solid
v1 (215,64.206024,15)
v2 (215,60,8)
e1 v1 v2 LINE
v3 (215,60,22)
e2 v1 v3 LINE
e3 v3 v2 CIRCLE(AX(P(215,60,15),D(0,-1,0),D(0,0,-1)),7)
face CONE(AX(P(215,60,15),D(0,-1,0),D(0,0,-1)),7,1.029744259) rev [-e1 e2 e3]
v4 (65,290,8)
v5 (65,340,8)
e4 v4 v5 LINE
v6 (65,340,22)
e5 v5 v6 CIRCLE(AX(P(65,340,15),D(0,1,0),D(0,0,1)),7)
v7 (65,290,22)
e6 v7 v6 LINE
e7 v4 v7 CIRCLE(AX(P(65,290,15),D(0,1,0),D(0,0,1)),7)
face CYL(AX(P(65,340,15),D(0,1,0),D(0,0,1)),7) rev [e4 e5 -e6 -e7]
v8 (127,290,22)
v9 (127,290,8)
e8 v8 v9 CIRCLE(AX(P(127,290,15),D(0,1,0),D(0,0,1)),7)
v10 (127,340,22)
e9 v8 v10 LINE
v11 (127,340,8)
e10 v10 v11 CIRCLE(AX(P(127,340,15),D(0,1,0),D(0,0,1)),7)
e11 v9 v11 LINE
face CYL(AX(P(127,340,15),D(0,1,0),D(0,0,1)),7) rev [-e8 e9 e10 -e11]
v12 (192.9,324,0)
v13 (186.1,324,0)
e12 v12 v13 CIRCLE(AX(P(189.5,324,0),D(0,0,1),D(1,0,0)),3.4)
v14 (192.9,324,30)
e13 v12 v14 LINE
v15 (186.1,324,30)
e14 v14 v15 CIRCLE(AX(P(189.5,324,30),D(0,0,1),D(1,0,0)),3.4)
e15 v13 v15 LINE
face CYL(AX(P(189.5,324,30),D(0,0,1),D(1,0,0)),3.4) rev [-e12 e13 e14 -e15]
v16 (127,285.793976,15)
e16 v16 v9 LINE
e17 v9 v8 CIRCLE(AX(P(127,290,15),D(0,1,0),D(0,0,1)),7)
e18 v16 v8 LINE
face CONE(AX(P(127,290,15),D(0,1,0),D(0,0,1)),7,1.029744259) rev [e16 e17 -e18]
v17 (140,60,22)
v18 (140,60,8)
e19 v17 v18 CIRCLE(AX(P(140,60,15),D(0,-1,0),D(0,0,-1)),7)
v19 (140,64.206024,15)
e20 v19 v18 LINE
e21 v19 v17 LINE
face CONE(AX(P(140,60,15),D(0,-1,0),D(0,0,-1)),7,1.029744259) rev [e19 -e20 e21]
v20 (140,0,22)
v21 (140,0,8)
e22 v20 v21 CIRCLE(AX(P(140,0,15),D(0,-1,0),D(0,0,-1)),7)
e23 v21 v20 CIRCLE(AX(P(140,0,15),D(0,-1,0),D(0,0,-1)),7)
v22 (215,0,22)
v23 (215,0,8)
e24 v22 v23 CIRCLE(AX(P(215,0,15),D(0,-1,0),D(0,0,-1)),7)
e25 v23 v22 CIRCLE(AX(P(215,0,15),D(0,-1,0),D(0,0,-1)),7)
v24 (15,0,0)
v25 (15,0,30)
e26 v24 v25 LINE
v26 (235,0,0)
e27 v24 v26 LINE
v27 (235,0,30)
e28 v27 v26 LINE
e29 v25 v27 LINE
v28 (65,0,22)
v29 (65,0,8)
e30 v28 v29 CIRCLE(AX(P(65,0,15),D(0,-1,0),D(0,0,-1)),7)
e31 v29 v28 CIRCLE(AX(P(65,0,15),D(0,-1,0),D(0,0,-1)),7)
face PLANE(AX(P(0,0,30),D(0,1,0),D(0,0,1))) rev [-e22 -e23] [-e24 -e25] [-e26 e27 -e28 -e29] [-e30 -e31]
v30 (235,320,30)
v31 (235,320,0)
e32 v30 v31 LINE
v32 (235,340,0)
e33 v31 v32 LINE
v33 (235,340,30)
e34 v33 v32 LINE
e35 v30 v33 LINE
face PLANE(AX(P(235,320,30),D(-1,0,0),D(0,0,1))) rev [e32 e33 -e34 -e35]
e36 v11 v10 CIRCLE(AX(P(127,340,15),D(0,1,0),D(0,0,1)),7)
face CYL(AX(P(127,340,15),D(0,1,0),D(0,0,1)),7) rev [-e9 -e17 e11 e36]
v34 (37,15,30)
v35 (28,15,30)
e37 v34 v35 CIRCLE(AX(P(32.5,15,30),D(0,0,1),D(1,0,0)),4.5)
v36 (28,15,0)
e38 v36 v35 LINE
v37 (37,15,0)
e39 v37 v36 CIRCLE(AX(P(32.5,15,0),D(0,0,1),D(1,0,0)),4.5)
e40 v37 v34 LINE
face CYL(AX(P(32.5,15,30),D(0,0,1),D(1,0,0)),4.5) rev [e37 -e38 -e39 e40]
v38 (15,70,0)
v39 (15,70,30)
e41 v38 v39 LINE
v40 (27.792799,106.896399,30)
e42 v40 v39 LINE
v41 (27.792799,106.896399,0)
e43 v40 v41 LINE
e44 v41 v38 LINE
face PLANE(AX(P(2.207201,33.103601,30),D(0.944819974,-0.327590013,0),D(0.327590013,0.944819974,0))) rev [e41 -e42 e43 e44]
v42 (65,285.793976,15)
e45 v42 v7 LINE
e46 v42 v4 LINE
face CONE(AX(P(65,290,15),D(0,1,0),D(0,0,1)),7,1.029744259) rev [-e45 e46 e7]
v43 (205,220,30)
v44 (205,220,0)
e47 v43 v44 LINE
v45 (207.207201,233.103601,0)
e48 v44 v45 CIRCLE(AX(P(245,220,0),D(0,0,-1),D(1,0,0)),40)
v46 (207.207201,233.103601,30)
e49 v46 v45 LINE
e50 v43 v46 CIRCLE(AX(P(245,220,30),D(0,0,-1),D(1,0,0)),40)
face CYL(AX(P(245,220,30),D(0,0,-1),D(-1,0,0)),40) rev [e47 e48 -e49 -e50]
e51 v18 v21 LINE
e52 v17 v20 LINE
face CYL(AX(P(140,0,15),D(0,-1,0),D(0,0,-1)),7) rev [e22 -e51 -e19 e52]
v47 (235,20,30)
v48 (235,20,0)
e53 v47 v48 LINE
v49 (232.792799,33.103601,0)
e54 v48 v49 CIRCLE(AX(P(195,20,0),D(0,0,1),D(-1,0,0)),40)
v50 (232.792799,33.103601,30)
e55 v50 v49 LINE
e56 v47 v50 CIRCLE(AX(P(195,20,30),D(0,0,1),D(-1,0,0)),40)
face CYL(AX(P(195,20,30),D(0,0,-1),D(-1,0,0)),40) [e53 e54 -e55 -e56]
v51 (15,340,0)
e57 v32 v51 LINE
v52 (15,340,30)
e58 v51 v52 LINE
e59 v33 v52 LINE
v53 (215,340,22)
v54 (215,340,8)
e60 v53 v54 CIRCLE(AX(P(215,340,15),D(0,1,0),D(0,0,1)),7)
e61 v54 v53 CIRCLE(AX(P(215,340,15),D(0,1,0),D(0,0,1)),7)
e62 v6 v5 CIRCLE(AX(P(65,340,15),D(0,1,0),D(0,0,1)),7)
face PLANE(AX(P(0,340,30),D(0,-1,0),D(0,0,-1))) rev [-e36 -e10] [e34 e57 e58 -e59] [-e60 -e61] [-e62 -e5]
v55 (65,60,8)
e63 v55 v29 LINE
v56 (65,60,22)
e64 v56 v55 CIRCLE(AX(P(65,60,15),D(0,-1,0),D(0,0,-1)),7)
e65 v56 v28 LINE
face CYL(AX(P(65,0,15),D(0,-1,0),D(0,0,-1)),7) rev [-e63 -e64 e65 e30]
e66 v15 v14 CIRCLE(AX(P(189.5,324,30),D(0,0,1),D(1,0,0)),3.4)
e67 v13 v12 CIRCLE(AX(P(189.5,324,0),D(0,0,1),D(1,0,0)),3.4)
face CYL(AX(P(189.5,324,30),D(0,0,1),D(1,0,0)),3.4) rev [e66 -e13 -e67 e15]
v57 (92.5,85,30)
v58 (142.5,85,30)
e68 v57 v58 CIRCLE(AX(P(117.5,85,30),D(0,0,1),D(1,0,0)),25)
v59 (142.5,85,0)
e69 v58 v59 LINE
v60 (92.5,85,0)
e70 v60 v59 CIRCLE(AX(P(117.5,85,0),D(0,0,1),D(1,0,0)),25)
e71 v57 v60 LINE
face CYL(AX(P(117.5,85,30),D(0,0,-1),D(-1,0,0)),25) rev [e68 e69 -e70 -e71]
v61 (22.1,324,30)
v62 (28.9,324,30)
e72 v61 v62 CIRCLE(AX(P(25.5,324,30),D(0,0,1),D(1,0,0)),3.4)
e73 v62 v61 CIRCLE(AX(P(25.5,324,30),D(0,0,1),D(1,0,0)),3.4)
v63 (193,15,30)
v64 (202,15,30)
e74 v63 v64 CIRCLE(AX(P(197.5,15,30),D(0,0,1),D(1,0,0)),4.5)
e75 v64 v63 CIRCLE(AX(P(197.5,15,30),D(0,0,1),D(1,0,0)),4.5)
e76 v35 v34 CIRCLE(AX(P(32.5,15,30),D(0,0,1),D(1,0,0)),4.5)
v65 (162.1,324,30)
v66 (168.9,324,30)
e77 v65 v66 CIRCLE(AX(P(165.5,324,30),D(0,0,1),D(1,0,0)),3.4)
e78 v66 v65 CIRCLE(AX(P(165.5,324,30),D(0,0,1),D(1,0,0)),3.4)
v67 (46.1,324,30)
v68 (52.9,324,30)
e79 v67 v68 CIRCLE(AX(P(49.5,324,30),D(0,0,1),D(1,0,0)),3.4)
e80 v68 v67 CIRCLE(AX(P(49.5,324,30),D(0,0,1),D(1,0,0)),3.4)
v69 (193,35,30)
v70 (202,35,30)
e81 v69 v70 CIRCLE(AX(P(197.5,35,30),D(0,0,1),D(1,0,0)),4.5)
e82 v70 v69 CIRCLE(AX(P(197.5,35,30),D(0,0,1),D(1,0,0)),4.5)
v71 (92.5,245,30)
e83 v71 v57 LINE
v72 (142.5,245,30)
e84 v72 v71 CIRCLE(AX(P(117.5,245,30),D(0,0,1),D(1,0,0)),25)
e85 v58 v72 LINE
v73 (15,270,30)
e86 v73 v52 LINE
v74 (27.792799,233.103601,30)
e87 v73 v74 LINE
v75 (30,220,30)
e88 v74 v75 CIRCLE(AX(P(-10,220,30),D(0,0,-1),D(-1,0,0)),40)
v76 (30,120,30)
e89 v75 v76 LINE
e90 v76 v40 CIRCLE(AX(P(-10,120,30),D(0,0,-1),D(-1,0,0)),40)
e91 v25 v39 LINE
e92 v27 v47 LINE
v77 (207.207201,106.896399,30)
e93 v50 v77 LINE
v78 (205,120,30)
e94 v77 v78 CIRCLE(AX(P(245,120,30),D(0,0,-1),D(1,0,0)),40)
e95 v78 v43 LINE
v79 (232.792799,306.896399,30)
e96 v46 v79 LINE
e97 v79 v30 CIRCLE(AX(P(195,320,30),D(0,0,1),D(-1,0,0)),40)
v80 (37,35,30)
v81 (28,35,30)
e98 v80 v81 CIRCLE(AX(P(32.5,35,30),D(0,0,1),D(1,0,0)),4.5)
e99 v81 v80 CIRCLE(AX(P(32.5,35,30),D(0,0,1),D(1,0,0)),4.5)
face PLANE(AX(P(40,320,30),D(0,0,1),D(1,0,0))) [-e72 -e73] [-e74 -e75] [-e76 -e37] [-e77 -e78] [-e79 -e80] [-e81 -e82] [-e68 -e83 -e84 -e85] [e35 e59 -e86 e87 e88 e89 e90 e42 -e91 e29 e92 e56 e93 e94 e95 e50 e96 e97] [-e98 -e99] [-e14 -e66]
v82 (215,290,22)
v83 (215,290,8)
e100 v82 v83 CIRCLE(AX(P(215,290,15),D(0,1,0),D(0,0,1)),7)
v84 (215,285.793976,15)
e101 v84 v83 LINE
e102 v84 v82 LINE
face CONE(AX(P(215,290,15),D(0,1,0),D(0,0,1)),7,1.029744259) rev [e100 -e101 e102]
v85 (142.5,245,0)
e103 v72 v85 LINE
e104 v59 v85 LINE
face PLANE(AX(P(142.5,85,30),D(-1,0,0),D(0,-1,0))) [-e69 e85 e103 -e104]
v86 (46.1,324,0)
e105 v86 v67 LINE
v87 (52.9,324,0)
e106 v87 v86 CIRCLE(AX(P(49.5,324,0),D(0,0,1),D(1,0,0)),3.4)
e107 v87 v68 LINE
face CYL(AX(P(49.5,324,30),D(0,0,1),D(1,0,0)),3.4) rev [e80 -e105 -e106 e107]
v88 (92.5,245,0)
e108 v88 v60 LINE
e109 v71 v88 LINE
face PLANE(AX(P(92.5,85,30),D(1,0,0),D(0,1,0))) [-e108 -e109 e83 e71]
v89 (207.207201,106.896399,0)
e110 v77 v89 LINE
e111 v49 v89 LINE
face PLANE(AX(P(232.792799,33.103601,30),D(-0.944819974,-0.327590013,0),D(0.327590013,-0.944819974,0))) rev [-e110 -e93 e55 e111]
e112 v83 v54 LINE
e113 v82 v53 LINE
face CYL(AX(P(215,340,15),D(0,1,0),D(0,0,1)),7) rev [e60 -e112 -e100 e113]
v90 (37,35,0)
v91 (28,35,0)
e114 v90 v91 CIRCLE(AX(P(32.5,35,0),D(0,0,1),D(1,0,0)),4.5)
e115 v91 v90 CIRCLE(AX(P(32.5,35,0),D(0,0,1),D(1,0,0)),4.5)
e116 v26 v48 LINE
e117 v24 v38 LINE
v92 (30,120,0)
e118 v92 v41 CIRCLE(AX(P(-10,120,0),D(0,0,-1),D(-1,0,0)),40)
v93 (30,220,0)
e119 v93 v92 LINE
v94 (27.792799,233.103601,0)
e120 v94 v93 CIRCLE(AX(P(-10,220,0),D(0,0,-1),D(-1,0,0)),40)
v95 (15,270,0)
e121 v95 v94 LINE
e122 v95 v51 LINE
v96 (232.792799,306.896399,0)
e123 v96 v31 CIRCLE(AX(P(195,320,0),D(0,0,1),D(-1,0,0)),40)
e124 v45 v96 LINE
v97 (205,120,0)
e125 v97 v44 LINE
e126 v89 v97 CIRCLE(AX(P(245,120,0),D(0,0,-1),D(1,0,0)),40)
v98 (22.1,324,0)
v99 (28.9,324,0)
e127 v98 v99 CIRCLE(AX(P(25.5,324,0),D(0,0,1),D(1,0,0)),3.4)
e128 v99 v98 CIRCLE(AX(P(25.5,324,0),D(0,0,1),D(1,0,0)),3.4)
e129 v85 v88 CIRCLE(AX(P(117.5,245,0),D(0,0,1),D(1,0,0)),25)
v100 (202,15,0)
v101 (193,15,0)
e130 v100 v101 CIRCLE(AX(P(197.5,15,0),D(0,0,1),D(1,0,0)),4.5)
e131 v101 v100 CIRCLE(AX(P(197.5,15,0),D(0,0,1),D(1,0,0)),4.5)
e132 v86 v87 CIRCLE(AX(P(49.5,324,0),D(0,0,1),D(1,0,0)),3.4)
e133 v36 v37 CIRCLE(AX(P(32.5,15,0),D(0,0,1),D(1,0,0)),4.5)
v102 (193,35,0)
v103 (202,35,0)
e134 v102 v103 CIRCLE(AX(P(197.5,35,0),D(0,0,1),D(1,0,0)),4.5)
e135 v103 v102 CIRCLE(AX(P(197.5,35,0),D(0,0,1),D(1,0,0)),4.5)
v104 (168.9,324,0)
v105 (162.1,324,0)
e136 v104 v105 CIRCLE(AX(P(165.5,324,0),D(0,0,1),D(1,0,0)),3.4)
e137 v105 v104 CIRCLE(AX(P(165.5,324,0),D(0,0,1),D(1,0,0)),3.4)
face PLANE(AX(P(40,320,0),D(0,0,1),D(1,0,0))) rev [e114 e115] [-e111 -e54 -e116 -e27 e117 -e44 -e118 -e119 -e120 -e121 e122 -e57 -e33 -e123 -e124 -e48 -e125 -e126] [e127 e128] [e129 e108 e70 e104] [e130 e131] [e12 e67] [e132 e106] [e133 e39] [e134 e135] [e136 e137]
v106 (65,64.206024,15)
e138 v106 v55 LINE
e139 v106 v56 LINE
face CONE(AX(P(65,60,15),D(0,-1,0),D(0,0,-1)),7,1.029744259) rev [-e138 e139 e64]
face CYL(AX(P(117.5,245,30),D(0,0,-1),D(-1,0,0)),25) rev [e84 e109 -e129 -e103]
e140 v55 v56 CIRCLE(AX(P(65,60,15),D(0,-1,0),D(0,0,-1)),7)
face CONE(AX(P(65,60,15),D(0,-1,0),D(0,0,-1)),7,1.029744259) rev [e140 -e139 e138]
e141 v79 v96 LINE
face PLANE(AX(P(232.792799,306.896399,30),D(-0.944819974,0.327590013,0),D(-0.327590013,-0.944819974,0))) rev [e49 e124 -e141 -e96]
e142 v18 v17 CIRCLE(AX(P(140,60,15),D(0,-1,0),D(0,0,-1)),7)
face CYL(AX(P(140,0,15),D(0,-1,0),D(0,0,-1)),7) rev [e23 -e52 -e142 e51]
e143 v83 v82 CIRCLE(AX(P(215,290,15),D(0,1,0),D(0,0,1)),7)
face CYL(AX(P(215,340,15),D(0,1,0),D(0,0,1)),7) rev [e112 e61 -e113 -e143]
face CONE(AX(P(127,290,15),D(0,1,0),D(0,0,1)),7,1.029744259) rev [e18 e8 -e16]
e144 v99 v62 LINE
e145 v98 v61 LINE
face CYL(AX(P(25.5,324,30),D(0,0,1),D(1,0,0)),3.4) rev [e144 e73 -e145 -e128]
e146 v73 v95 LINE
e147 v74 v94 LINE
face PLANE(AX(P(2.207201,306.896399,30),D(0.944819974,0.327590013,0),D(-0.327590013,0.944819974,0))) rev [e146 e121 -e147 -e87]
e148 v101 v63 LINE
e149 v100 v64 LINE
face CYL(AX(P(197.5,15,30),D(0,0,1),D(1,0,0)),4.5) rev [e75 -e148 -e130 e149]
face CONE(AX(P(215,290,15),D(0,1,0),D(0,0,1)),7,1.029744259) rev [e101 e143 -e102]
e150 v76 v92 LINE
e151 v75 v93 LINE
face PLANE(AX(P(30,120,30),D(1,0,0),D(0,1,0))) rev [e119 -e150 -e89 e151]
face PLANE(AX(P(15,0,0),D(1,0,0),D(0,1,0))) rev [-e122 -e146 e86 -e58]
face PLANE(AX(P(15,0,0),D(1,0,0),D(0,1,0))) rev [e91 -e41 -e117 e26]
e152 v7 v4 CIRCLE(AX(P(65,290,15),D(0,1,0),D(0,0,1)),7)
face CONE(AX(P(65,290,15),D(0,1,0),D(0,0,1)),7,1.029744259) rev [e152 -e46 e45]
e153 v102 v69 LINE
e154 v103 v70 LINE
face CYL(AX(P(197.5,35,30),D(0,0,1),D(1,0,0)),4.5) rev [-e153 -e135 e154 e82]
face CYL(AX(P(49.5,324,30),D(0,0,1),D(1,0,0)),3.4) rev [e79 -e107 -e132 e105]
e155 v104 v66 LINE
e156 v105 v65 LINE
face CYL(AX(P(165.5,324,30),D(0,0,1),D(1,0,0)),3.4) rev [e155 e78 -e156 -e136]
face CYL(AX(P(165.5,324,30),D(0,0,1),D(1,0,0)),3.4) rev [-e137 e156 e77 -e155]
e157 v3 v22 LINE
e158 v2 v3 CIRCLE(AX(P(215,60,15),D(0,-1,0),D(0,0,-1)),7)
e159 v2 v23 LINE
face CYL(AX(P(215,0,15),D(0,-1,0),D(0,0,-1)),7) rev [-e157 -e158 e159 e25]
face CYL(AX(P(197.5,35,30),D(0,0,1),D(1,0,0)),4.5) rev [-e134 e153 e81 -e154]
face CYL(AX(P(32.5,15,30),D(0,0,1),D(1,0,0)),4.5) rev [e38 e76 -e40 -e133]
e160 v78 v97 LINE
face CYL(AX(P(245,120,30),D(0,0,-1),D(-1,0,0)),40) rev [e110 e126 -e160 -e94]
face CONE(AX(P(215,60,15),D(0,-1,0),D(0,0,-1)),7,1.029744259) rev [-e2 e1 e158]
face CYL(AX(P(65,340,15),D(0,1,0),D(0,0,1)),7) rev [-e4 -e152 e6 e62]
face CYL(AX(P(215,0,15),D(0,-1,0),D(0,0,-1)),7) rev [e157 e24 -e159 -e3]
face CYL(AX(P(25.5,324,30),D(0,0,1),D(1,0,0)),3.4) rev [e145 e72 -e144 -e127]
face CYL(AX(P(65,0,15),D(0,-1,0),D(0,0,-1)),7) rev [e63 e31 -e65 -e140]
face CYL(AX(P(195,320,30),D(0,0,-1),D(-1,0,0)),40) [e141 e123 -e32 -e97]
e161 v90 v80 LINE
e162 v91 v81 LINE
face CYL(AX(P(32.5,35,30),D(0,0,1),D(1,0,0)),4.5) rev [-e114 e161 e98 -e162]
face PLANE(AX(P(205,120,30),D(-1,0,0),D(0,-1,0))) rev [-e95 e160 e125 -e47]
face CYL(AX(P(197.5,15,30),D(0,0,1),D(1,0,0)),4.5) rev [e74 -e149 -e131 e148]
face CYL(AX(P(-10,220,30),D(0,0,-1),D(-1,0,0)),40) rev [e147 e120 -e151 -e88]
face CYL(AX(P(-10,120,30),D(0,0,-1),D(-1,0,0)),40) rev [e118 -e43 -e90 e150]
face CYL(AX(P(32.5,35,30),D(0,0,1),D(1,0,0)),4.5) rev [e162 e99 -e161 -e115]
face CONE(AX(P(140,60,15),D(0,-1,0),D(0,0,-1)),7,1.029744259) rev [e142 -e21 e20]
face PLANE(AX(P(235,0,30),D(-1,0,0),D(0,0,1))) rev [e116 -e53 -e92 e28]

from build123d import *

# Parameters (mm, degrees)
BOSS_EXTRUDE1_DEPTH      = 30
SKETCH4_W                = 15
SKETCH4_H                = 340
CUT_EXTRUDE1_DEPTH       = 415.3971525
M16_TAPPED_HOLE3_D       = 14
M16_TAPPED_HOLE3_DEPTH   = 60
M16_TAPPED_HOLE3_TIP     = 4.206024333
M16_TAPPED_HOLE2_D       = 14
M16_TAPPED_HOLE2_DEPTH   = 50
M16_TAPPED_HOLE2_TIP     = 4.206024333
M8_TAPPED_HOLE1_D        = 6.8
F_9_0_9_DIAMETER_HOLE1_D = 9


with BuildPart() as part:
    # Sketch1 → Boss-Extrude1 (new body)
    with BuildSketch(Plane.XY):
        with BuildLine():
            Line((0, 0), (235, 0))
            Line((235, 0), (235, 20))
            ThreePointArc((235, 20), (234.444340269, 26.644096684), (232.792798963, 33.103600519))
            Line((232.792798963, 33.103600519), (207.207201037, 106.896399481))
            ThreePointArc((207.207201037, 106.896399481), (205.555659731, 113.355903316), (205, 120))
            Line((205, 120), (205, 220))
            ThreePointArc((205, 220), (205.555659731, 226.644096684), (207.207201037, 233.103600519))
            Line((207.207201037, 233.103600519), (232.792798963, 306.896399481))
            ThreePointArc((232.792798963, 306.896399481), (234.444340269, 313.355903316), (235, 320))
            Line((235, 320), (235, 340))
            Line((235, 340), (0, 340))
            Line((0, 340), (0, 320))
            ThreePointArc((0, 320), (0.555659731, 313.355903316), (2.207201037, 306.896399481))
            Line((2.207201037, 306.896399481), (27.792798963, 233.103600519))
            ThreePointArc((27.792798963, 233.103600519), (29.444340269, 226.644096684), (30, 220))
            Line((30, 220), (30, 120))
            ThreePointArc((30, 120), (29.444340269, 113.355903316), (27.792798963, 106.896399481))
            Line((27.792798963, 106.896399481), (2.207201037, 33.103600519))
            ThreePointArc((2.207201037, 33.103600519), (0.555659731, 26.644096684), (0, 20))
            Line((0, 20), (0, 0))
        make_face()
        with BuildLine():
            Line((92.5, 85), (92.5, 245))
            ThreePointArc((92.5, 245), (117.5, 270), (142.5, 245))
            Line((142.5, 245), (142.5, 85))
            ThreePointArc((142.5, 85), (117.5, 60), (92.5, 85))
        make_face(mode=Mode.SUBTRACT)
    extrude(amount=BOSS_EXTRUDE1_DEPTH)

    # Sketch4 → Cut-Extrude1 (cut, through all)
    with BuildSketch(Plane.XY.offset(30)):
        with Locations((7.5, 170)):
            Rectangle(SKETCH4_W, SKETCH4_H)
    extrude(amount=-CUT_EXTRUDE1_DEPTH, mode=Mode.SUBTRACT)

    # M16 Tapped Hole3
    with Locations(Plane(origin=(0, 0, 0), x_dir=(-1, 0, 0), z_dir=(0, -1, 0))):
        with Locations((-215, -15), (-65, -15), (-140, -15)):
            Hole(M16_TAPPED_HOLE3_D / 2, depth=M16_TAPPED_HOLE3_DEPTH)
            with Locations((0, 0, -(M16_TAPPED_HOLE3_DEPTH + M16_TAPPED_HOLE3_TIP / 2))):  # 118° drill point
                Cone(0, M16_TAPPED_HOLE3_D / 2, M16_TAPPED_HOLE3_TIP, mode=Mode.SUBTRACT)

    # M16 Tapped Hole2
    with Locations(Plane(origin=(0, 340, 0), x_dir=(1, 0, 0), z_dir=(0, 1, 0))):
        with Locations((215, -15), (65, -15), (127, -15)):
            Hole(M16_TAPPED_HOLE2_D / 2, depth=M16_TAPPED_HOLE2_DEPTH)
            with Locations((0, 0, -(M16_TAPPED_HOLE2_DEPTH + M16_TAPPED_HOLE2_TIP / 2))):  # 118° drill point
                Cone(0, M16_TAPPED_HOLE2_D / 2, M16_TAPPED_HOLE2_TIP, mode=Mode.SUBTRACT)

    # M8 Tapped Hole1 (through all)
    with Locations(Plane.XY.offset(30)):
        with Locations((25.5, 324), (49.5, 324), (189.5, 324), (165.5, 324)):
            Hole(M8_TAPPED_HOLE1_D / 2)

    # Ø9.0 (9) Diameter Hole1 (through all)
    with Locations(Plane.XY.offset(30)):
        with Locations((197.5, 15), (197.5, 35), (32.5, 15), (32.5, 35)):
            Hole(F_9_0_9_DIAMETER_HOLE1_D / 2)


solid = part.part
